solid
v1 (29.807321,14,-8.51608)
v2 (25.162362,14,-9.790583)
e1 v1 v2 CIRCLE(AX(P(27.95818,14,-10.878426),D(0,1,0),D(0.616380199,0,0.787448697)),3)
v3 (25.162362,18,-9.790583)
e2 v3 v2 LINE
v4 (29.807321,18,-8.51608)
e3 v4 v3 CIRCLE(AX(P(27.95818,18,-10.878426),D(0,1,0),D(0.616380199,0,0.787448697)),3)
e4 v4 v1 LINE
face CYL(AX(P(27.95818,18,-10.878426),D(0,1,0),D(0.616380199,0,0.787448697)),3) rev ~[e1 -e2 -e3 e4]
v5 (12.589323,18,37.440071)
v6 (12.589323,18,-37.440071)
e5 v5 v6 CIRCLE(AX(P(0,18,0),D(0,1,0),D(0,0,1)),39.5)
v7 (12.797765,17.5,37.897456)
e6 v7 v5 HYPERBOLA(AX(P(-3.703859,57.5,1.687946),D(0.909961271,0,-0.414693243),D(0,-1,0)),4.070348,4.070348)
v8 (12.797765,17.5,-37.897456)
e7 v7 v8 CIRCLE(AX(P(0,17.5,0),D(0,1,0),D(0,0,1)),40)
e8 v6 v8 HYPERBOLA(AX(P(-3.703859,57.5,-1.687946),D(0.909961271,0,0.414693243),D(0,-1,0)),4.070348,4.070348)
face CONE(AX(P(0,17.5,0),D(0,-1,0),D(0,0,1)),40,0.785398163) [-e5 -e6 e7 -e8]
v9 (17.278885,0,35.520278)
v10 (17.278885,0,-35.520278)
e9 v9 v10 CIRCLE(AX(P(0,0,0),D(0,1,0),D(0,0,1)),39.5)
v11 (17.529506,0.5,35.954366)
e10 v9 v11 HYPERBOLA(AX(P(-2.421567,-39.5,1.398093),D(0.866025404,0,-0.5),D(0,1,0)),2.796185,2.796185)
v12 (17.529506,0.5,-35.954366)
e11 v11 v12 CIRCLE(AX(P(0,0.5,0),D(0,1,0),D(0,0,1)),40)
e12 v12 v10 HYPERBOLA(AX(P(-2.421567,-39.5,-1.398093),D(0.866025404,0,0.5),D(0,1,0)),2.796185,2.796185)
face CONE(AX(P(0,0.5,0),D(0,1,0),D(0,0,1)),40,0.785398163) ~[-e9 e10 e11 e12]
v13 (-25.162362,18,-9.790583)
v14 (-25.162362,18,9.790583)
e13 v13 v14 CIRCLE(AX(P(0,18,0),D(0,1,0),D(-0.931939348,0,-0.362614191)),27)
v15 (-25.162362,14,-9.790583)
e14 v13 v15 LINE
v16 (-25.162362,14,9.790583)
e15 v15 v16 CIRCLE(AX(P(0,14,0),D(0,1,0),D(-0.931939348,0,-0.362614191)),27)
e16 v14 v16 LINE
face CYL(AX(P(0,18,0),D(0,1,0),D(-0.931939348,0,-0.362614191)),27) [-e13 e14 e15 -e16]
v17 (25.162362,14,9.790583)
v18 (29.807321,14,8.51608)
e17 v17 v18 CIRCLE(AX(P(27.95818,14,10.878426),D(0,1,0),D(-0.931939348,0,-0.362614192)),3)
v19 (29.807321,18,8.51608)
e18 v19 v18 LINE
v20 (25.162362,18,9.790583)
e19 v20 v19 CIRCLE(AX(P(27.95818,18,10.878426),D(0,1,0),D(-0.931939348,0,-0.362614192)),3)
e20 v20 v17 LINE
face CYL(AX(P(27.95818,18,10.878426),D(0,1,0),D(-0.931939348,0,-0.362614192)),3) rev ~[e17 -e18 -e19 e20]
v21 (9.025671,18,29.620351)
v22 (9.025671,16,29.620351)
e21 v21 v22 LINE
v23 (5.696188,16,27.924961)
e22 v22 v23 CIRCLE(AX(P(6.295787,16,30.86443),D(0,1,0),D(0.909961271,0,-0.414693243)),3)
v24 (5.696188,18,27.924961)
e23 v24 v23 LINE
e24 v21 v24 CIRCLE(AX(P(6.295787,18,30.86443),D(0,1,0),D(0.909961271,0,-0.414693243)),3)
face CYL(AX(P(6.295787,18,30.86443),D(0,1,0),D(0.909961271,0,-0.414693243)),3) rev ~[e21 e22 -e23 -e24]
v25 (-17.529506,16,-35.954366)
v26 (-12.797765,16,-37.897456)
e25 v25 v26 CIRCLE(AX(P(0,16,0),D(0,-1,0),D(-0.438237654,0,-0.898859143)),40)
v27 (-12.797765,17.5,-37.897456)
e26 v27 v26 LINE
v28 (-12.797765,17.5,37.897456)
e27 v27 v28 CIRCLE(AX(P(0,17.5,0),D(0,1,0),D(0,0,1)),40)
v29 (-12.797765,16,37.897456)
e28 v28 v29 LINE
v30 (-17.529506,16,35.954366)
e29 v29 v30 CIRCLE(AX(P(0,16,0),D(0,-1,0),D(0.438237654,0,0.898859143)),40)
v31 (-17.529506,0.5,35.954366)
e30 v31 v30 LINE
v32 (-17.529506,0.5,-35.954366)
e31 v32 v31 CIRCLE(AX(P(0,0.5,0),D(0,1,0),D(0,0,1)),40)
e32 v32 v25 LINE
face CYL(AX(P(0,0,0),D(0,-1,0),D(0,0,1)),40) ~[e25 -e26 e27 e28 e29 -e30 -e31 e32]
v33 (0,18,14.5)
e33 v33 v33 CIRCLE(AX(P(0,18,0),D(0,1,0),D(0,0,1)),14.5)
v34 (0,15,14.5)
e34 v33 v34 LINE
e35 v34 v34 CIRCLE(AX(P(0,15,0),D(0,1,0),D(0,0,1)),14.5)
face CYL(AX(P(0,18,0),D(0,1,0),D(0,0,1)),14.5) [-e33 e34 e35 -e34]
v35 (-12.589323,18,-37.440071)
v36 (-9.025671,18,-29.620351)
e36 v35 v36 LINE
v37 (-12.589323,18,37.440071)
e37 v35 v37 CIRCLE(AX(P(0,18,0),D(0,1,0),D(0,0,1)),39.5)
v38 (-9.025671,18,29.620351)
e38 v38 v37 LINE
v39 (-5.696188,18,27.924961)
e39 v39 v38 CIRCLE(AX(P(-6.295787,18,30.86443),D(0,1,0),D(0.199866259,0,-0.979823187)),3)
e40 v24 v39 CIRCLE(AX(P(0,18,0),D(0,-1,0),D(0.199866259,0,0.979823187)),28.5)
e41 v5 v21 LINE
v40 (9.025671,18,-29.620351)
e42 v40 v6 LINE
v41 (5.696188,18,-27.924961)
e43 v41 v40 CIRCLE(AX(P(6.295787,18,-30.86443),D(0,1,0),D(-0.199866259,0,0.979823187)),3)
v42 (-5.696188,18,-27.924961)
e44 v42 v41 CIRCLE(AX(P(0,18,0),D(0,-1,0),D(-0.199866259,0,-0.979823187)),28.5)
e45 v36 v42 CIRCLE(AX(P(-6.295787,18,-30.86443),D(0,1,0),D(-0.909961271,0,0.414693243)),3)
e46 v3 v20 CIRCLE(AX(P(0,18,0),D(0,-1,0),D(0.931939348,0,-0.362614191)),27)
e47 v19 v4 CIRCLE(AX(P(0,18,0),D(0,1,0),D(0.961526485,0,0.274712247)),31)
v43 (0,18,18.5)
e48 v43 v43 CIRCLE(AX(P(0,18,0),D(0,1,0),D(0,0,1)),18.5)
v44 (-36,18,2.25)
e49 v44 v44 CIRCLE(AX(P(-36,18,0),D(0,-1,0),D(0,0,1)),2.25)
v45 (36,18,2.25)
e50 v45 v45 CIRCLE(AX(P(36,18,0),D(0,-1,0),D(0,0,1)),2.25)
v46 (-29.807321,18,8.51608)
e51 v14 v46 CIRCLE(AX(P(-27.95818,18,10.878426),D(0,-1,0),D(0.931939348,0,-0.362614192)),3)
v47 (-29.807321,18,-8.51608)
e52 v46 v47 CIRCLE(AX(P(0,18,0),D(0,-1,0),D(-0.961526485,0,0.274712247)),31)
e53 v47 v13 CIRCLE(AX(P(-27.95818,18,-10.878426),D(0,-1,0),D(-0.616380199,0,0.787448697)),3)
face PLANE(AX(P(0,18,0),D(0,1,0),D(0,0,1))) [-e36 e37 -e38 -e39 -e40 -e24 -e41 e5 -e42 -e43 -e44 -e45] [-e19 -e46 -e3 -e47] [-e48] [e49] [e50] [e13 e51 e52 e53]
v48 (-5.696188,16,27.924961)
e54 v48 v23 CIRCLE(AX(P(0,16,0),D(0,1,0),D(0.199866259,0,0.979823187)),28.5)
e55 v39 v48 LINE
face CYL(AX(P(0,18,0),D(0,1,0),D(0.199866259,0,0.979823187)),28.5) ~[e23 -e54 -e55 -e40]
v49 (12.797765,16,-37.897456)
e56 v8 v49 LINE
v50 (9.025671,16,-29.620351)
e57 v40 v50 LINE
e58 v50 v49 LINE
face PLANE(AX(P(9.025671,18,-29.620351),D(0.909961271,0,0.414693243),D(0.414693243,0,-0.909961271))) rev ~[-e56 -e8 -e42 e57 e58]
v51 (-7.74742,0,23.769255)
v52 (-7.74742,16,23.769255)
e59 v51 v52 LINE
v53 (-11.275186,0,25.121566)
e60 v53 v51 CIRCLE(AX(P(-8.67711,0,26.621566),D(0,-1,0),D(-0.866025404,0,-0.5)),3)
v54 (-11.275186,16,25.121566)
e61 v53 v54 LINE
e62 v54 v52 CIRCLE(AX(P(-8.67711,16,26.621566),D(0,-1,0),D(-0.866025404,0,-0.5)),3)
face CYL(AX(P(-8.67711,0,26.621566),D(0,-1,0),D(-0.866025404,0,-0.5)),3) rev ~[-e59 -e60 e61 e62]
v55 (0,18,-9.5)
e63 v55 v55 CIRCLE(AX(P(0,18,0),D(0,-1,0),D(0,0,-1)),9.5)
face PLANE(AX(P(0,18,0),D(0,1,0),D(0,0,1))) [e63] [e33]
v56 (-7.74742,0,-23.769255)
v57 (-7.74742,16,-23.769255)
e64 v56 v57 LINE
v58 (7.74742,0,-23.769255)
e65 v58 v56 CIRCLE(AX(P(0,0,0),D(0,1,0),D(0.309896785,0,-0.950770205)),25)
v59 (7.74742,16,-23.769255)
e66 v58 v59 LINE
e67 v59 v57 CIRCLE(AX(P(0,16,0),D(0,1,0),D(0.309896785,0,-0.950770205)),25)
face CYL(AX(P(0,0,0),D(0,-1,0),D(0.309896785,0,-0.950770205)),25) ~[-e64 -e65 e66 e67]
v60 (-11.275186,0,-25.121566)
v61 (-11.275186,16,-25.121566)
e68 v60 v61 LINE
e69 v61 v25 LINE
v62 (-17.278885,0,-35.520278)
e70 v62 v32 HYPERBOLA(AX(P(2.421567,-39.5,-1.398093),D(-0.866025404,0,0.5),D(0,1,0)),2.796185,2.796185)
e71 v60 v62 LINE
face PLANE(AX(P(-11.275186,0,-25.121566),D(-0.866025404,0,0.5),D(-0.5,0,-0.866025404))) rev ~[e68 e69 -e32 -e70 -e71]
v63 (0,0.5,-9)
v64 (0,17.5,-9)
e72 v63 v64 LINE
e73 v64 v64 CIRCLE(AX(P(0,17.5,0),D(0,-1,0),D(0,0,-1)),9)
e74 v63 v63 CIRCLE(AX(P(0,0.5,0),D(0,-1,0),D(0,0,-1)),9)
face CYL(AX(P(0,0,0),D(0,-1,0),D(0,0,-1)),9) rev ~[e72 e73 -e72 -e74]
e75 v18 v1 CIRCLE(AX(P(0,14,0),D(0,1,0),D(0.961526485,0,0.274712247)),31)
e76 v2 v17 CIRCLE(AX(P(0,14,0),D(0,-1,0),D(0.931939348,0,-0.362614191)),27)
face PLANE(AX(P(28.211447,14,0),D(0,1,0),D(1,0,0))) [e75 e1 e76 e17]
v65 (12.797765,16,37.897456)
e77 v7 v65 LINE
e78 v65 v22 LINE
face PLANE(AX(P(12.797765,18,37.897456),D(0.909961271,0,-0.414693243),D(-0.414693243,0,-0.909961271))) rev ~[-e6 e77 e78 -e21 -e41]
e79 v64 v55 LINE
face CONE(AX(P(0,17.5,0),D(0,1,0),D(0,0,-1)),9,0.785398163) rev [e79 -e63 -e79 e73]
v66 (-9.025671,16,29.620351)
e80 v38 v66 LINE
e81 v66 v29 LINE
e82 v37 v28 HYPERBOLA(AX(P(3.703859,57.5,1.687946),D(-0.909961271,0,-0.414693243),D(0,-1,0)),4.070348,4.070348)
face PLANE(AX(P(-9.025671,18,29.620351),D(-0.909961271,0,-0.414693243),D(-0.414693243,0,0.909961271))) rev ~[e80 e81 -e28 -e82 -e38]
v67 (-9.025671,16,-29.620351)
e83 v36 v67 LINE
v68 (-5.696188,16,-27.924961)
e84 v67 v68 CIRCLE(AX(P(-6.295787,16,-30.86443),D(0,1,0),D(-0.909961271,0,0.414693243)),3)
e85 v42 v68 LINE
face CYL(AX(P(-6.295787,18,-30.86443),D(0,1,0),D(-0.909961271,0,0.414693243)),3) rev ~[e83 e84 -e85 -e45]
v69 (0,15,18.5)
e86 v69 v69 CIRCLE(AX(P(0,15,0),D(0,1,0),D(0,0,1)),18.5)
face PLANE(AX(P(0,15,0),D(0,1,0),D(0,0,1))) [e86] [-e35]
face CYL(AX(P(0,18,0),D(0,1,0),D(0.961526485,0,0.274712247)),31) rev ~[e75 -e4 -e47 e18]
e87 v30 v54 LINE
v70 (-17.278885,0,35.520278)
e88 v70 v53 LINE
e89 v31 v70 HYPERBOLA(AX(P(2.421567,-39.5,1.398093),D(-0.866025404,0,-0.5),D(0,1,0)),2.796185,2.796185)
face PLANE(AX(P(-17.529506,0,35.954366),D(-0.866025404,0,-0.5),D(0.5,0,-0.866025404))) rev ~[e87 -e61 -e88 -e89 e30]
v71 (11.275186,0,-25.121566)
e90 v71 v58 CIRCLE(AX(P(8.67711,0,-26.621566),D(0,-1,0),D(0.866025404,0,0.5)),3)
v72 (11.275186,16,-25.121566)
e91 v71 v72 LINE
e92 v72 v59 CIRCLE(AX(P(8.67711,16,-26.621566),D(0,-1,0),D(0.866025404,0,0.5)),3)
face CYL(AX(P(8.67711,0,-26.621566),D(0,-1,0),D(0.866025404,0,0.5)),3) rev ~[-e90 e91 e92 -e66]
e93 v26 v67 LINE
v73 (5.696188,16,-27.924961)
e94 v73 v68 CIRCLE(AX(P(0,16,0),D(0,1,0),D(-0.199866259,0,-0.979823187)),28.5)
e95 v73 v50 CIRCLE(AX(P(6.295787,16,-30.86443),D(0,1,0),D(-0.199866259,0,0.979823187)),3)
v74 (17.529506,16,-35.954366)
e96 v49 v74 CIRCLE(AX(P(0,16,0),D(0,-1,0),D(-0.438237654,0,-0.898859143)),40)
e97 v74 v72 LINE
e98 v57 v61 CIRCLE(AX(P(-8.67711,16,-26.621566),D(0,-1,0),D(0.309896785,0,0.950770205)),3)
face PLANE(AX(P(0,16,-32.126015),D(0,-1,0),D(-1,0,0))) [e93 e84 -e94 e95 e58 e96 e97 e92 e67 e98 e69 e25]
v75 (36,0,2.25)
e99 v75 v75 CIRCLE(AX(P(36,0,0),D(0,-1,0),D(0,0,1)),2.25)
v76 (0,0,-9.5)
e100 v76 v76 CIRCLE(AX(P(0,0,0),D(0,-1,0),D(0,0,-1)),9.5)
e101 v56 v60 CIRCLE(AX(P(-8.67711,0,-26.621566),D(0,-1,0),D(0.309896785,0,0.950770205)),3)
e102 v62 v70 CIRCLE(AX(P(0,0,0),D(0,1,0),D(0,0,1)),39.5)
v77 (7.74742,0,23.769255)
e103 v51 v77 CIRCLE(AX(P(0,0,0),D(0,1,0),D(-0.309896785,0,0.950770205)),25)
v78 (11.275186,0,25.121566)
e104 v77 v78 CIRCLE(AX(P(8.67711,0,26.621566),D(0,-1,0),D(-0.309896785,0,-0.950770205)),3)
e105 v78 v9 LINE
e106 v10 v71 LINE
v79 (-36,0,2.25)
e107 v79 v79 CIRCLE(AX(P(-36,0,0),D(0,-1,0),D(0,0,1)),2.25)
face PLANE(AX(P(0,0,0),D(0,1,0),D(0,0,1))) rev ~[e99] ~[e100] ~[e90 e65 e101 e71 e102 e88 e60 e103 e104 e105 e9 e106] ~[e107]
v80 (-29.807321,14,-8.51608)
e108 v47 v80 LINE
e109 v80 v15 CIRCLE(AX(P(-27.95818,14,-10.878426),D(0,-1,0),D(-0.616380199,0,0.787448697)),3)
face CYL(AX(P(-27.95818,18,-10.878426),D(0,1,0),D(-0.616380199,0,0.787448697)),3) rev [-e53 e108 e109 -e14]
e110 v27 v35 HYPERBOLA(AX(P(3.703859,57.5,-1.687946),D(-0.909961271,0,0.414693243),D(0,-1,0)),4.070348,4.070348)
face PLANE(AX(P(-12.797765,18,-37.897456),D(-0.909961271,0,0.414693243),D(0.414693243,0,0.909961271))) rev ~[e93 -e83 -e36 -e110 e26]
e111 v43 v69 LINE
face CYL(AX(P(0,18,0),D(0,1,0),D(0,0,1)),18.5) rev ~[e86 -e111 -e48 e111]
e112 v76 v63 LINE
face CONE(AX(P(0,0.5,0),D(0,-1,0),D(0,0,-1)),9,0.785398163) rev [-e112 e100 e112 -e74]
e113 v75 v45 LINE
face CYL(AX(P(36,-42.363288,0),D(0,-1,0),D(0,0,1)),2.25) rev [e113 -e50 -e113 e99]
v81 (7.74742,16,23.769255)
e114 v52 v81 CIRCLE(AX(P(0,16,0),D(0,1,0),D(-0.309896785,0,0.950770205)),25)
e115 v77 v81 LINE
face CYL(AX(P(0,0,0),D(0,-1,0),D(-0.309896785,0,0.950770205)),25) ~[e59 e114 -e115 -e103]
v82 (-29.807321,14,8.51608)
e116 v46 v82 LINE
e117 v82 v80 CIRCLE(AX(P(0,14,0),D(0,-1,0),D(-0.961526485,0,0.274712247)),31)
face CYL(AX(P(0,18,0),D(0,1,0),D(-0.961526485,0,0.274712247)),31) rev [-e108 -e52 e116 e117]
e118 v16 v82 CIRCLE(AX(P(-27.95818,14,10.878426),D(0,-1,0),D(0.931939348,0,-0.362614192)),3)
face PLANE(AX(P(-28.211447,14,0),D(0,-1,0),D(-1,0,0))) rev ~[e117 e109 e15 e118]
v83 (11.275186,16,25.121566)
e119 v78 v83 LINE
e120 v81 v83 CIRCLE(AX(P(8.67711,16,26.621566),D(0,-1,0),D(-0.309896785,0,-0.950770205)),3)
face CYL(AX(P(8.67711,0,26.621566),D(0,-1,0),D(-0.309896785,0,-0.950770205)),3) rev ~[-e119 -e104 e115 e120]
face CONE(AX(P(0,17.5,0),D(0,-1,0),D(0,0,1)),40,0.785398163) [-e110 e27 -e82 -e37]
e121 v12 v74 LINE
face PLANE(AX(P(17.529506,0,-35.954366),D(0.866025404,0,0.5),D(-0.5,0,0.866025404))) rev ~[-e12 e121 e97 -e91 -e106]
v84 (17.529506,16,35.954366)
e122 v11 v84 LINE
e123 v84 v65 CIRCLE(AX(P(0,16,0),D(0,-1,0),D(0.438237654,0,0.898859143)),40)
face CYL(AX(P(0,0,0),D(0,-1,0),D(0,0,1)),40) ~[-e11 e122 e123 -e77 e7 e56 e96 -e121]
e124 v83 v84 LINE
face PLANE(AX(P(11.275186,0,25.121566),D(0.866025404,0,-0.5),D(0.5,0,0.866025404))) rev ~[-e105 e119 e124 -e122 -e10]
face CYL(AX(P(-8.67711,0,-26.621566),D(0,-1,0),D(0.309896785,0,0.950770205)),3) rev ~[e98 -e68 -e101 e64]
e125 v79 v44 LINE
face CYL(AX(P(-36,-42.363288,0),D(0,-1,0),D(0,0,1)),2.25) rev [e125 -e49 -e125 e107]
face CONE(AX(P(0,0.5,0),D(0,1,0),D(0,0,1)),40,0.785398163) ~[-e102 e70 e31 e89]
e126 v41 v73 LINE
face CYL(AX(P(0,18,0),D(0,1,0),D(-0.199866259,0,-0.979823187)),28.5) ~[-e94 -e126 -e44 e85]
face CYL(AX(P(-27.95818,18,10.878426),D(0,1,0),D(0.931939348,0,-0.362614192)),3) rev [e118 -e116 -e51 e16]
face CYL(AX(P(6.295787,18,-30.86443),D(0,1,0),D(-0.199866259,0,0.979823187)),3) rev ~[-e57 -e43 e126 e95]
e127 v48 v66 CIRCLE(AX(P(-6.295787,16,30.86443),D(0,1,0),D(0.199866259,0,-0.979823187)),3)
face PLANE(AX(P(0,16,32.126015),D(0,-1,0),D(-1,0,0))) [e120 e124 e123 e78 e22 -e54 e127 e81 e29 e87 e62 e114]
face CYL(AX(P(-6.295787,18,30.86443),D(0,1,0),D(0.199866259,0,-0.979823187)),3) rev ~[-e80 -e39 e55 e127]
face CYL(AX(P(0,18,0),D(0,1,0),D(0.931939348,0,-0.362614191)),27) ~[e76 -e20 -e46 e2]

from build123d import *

# Parameters (mm, degrees)
SKETCH1_R               = 40
BOSS_EXTRUDE1_DEPTH     = 18
CHAMFER2_SIZE           = 0.5
CUT_EXTRUDE1_DEPTH      = 60.363288319
CUT_EXTRUDE1_DEPTH_BACK = 60.363288319
SKETCH2_R               = 2.25
CUT_EXTRUDE2_DEPTH      = 4
CUT_EXTRUDE3_DEPTH      = 60.363288319
SKETCH5_R               = 9
CUT_EXTRUDE4_DEPTH      = 58.967380496
CUT_EXTRUDE5_DEPTH      = 16
SKETCH7_R               = 18.5
SKETCH7_R_2             = 14.5
CUT_EXTRUDE6_DEPTH      = 3
CHAMFER1_SIZE           = 0.5


with BuildPart() as part:
    # Sketch1 → Boss-Extrude1 (new body)
    with BuildSketch(Plane(origin=(0, 0, 0), x_dir=(1, 0, 0), z_dir=(0, 1, 0))):
        with Locations(Location((0, 0, 0), (0, 0, 270))):
            Circle(SKETCH1_R)
    extrude(amount=BOSS_EXTRUDE1_DEPTH)

    # Chamfer2
    chamfer2_edges = [part.edges().sort_by_distance(p)[0] for p in [
        (0, 0, -40),
        (0, 18, -40),
    ]]
    chamfer(chamfer2_edges, length=CHAMFER2_SIZE)

    # Sketch2 → Cut-Extrude1 (cut, two sides: drawn at the far end of the back side and taken through both)
    with BuildSketch(Plane(origin=(0, 18, 0), x_dir=(1, 0, 0), z_dir=(0, 1, 0)).offset(-CUT_EXTRUDE1_DEPTH_BACK)):
        with Locations(Location((36, 0, 0), (0, 0, 270))):
            Circle(SKETCH2_R)
        with Locations(Location((-36, 0, 0), (0, 0, 270))):
            Circle(SKETCH2_R)
    extrude(amount=CUT_EXTRUDE1_DEPTH + CUT_EXTRUDE1_DEPTH_BACK, mode=Mode.SUBTRACT)

    # Sketch3 → Cut-Extrude2 (cut)
    with BuildSketch(Plane(origin=(0, 18, 0), x_dir=(1, 0, 0), z_dir=(0, 1, 0))):
        with BuildLine():
            ThreePointArc((-25.162362394, 9.790583167), (-27, 0), (-25.162362394, -9.790583167))
            ThreePointArc((-25.162362394, -9.790583167), (-28.751993608, -13.771496887), (-29.807321036, -8.516079652))
            ThreePointArc((-29.807321036, -8.516079652), (-31, 0), (-29.807321036, 8.516079652))
            ThreePointArc((-29.807321036, 8.516079652), (-28.751993608, 13.771496887), (-25.162362394, 9.790583167))
        make_face()
        with BuildLine():
            ThreePointArc((25.162362394, -9.790583167), (28.751993608, -13.771496887), (29.807321036, -8.516079652))
            ThreePointArc((29.807321036, -8.516079652), (31, 0), (29.807321036, 8.516079652))
            ThreePointArc((29.807321036, 8.516079652), (28.751993608, 13.771496887), (25.162362394, 9.790583167))
            ThreePointArc((25.162362394, 9.790583167), (27, 0), (25.162362394, -9.790583167))
        make_face()
    extrude(amount=-CUT_EXTRUDE2_DEPTH, mode=Mode.SUBTRACT)

    # Sketch4 → Cut-Extrude3 (cut, through all)
    with BuildSketch(Plane(origin=(0, 18, 0), x_dir=(1, 0, 0), z_dir=(0, 1, 0))):
        with BuildLine():
            Line((-12.797765369, 37.8974564), (-9.02567097, 29.620350674))
            ThreePointArc((-9.02567097, 29.620350674), (-7.657078917, 28.191064594), (-5.696188381, 27.92496084))
            ThreePointArc((-5.696188381, 27.92496084), (0, 28.5), (5.696188381, 27.92496084))
            ThreePointArc((5.696188381, 27.92496084), (7.657078917, 28.191064594), (9.02567097, 29.620350674))
            Line((9.02567097, 29.620350674), (12.797765369, 37.8974564))
            ThreePointArc((12.797765369, 37.8974564), (0, 40), (-12.797765369, 37.8974564))
        make_face()
        with BuildLine():
            Line((12.797765369, -37.8974564), (9.02567097, -29.620350674))
            ThreePointArc((9.02567097, -29.620350674), (7.657078917, -28.191064594), (5.696188381, -27.92496084))
            ThreePointArc((5.696188381, -27.92496084), (0, -28.5), (-5.696188381, -27.92496084))
            ThreePointArc((-5.696188381, -27.92496084), (-7.657078917, -28.191064594), (-9.02567097, -29.620350674))
            Line((-9.02567097, -29.620350674), (-12.797765369, -37.8974564))
            ThreePointArc((-12.797765369, -37.8974564), (0, -40), (12.797765369, -37.8974564))
        make_face()
    extrude(amount=-CUT_EXTRUDE3_DEPTH, mode=Mode.SUBTRACT)

    # Sketch5 → Cut-Extrude4 (cut, through all)
    with BuildSketch(Plane(origin=(0, 0, 0), x_dir=(-1, 0, 0), z_dir=(0, -1, 0))):
        with Locations(Location((0, 0, 0), (0, 0, 90))):
            Circle(SKETCH5_R)
    extrude(amount=-CUT_EXTRUDE4_DEPTH, mode=Mode.SUBTRACT)

    # Sketch6 → Cut-Extrude5 (cut)
    with BuildSketch(Plane(origin=(0, 0, 0), x_dir=(-1, 0, 0), z_dir=(0, -1, 0))):
        with BuildLine():
            Line((17.529506166, -35.95436571), (11.275186187, -25.12156574))
            ThreePointArc((11.275186187, -25.12156574), (9.750918079, -23.820327414), (7.747419621, -23.769255125))
            ThreePointArc((7.747419621, -23.769255125), (0, -25), (-7.747419621, -23.769255125))
            ThreePointArc((-7.747419621, -23.769255125), (-9.750918079, -23.820327414), (-11.275186187, -25.12156574))
            Line((-11.275186187, -25.12156574), (-17.529506166, -35.95436571))
            ThreePointArc((-17.529506166, -35.95436571), (0, -40), (17.529506166, -35.95436571))
        make_face()
        with BuildLine():
            Line((-17.529506166, 35.95436571), (-11.275186187, 25.12156574))
            ThreePointArc((-11.275186187, 25.12156574), (-9.750918079, 23.820327414), (-7.747419621, 23.769255125))
            ThreePointArc((-7.747419621, 23.769255125), (0, 25), (7.747419621, 23.769255125))
            ThreePointArc((7.747419621, 23.769255125), (9.750918079, 23.820327414), (11.275186187, 25.12156574))
            Line((11.275186187, 25.12156574), (17.529506166, 35.95436571))
            ThreePointArc((17.529506166, 35.95436571), (0, 40), (-17.529506166, 35.95436571))
        make_face()
    extrude(amount=-CUT_EXTRUDE5_DEPTH, mode=Mode.SUBTRACT)

    # Sketch7 → Cut-Extrude6 (cut)
    with BuildSketch(Plane(origin=(0, 18, 0), x_dir=(1, 0, 0), z_dir=(0, 1, 0))):
        with Locations(Location((0, 0, 0), (0, 0, 270))):
            Circle(SKETCH7_R)
        with Locations(Location((0, 0, 0), (0, 0, 270))):
            Circle(SKETCH7_R_2, mode=Mode.SUBTRACT)
    extrude(amount=-CUT_EXTRUDE6_DEPTH, mode=Mode.SUBTRACT)

    # Chamfer1
    chamfer1_edges = [part.edges().sort_by_distance(p)[0] for p in [
        (0, 18, 9),
        (0, 0, 9),
    ]]
    chamfer(chamfer1_edges, length=CHAMFER1_SIZE)


solid = part.part
